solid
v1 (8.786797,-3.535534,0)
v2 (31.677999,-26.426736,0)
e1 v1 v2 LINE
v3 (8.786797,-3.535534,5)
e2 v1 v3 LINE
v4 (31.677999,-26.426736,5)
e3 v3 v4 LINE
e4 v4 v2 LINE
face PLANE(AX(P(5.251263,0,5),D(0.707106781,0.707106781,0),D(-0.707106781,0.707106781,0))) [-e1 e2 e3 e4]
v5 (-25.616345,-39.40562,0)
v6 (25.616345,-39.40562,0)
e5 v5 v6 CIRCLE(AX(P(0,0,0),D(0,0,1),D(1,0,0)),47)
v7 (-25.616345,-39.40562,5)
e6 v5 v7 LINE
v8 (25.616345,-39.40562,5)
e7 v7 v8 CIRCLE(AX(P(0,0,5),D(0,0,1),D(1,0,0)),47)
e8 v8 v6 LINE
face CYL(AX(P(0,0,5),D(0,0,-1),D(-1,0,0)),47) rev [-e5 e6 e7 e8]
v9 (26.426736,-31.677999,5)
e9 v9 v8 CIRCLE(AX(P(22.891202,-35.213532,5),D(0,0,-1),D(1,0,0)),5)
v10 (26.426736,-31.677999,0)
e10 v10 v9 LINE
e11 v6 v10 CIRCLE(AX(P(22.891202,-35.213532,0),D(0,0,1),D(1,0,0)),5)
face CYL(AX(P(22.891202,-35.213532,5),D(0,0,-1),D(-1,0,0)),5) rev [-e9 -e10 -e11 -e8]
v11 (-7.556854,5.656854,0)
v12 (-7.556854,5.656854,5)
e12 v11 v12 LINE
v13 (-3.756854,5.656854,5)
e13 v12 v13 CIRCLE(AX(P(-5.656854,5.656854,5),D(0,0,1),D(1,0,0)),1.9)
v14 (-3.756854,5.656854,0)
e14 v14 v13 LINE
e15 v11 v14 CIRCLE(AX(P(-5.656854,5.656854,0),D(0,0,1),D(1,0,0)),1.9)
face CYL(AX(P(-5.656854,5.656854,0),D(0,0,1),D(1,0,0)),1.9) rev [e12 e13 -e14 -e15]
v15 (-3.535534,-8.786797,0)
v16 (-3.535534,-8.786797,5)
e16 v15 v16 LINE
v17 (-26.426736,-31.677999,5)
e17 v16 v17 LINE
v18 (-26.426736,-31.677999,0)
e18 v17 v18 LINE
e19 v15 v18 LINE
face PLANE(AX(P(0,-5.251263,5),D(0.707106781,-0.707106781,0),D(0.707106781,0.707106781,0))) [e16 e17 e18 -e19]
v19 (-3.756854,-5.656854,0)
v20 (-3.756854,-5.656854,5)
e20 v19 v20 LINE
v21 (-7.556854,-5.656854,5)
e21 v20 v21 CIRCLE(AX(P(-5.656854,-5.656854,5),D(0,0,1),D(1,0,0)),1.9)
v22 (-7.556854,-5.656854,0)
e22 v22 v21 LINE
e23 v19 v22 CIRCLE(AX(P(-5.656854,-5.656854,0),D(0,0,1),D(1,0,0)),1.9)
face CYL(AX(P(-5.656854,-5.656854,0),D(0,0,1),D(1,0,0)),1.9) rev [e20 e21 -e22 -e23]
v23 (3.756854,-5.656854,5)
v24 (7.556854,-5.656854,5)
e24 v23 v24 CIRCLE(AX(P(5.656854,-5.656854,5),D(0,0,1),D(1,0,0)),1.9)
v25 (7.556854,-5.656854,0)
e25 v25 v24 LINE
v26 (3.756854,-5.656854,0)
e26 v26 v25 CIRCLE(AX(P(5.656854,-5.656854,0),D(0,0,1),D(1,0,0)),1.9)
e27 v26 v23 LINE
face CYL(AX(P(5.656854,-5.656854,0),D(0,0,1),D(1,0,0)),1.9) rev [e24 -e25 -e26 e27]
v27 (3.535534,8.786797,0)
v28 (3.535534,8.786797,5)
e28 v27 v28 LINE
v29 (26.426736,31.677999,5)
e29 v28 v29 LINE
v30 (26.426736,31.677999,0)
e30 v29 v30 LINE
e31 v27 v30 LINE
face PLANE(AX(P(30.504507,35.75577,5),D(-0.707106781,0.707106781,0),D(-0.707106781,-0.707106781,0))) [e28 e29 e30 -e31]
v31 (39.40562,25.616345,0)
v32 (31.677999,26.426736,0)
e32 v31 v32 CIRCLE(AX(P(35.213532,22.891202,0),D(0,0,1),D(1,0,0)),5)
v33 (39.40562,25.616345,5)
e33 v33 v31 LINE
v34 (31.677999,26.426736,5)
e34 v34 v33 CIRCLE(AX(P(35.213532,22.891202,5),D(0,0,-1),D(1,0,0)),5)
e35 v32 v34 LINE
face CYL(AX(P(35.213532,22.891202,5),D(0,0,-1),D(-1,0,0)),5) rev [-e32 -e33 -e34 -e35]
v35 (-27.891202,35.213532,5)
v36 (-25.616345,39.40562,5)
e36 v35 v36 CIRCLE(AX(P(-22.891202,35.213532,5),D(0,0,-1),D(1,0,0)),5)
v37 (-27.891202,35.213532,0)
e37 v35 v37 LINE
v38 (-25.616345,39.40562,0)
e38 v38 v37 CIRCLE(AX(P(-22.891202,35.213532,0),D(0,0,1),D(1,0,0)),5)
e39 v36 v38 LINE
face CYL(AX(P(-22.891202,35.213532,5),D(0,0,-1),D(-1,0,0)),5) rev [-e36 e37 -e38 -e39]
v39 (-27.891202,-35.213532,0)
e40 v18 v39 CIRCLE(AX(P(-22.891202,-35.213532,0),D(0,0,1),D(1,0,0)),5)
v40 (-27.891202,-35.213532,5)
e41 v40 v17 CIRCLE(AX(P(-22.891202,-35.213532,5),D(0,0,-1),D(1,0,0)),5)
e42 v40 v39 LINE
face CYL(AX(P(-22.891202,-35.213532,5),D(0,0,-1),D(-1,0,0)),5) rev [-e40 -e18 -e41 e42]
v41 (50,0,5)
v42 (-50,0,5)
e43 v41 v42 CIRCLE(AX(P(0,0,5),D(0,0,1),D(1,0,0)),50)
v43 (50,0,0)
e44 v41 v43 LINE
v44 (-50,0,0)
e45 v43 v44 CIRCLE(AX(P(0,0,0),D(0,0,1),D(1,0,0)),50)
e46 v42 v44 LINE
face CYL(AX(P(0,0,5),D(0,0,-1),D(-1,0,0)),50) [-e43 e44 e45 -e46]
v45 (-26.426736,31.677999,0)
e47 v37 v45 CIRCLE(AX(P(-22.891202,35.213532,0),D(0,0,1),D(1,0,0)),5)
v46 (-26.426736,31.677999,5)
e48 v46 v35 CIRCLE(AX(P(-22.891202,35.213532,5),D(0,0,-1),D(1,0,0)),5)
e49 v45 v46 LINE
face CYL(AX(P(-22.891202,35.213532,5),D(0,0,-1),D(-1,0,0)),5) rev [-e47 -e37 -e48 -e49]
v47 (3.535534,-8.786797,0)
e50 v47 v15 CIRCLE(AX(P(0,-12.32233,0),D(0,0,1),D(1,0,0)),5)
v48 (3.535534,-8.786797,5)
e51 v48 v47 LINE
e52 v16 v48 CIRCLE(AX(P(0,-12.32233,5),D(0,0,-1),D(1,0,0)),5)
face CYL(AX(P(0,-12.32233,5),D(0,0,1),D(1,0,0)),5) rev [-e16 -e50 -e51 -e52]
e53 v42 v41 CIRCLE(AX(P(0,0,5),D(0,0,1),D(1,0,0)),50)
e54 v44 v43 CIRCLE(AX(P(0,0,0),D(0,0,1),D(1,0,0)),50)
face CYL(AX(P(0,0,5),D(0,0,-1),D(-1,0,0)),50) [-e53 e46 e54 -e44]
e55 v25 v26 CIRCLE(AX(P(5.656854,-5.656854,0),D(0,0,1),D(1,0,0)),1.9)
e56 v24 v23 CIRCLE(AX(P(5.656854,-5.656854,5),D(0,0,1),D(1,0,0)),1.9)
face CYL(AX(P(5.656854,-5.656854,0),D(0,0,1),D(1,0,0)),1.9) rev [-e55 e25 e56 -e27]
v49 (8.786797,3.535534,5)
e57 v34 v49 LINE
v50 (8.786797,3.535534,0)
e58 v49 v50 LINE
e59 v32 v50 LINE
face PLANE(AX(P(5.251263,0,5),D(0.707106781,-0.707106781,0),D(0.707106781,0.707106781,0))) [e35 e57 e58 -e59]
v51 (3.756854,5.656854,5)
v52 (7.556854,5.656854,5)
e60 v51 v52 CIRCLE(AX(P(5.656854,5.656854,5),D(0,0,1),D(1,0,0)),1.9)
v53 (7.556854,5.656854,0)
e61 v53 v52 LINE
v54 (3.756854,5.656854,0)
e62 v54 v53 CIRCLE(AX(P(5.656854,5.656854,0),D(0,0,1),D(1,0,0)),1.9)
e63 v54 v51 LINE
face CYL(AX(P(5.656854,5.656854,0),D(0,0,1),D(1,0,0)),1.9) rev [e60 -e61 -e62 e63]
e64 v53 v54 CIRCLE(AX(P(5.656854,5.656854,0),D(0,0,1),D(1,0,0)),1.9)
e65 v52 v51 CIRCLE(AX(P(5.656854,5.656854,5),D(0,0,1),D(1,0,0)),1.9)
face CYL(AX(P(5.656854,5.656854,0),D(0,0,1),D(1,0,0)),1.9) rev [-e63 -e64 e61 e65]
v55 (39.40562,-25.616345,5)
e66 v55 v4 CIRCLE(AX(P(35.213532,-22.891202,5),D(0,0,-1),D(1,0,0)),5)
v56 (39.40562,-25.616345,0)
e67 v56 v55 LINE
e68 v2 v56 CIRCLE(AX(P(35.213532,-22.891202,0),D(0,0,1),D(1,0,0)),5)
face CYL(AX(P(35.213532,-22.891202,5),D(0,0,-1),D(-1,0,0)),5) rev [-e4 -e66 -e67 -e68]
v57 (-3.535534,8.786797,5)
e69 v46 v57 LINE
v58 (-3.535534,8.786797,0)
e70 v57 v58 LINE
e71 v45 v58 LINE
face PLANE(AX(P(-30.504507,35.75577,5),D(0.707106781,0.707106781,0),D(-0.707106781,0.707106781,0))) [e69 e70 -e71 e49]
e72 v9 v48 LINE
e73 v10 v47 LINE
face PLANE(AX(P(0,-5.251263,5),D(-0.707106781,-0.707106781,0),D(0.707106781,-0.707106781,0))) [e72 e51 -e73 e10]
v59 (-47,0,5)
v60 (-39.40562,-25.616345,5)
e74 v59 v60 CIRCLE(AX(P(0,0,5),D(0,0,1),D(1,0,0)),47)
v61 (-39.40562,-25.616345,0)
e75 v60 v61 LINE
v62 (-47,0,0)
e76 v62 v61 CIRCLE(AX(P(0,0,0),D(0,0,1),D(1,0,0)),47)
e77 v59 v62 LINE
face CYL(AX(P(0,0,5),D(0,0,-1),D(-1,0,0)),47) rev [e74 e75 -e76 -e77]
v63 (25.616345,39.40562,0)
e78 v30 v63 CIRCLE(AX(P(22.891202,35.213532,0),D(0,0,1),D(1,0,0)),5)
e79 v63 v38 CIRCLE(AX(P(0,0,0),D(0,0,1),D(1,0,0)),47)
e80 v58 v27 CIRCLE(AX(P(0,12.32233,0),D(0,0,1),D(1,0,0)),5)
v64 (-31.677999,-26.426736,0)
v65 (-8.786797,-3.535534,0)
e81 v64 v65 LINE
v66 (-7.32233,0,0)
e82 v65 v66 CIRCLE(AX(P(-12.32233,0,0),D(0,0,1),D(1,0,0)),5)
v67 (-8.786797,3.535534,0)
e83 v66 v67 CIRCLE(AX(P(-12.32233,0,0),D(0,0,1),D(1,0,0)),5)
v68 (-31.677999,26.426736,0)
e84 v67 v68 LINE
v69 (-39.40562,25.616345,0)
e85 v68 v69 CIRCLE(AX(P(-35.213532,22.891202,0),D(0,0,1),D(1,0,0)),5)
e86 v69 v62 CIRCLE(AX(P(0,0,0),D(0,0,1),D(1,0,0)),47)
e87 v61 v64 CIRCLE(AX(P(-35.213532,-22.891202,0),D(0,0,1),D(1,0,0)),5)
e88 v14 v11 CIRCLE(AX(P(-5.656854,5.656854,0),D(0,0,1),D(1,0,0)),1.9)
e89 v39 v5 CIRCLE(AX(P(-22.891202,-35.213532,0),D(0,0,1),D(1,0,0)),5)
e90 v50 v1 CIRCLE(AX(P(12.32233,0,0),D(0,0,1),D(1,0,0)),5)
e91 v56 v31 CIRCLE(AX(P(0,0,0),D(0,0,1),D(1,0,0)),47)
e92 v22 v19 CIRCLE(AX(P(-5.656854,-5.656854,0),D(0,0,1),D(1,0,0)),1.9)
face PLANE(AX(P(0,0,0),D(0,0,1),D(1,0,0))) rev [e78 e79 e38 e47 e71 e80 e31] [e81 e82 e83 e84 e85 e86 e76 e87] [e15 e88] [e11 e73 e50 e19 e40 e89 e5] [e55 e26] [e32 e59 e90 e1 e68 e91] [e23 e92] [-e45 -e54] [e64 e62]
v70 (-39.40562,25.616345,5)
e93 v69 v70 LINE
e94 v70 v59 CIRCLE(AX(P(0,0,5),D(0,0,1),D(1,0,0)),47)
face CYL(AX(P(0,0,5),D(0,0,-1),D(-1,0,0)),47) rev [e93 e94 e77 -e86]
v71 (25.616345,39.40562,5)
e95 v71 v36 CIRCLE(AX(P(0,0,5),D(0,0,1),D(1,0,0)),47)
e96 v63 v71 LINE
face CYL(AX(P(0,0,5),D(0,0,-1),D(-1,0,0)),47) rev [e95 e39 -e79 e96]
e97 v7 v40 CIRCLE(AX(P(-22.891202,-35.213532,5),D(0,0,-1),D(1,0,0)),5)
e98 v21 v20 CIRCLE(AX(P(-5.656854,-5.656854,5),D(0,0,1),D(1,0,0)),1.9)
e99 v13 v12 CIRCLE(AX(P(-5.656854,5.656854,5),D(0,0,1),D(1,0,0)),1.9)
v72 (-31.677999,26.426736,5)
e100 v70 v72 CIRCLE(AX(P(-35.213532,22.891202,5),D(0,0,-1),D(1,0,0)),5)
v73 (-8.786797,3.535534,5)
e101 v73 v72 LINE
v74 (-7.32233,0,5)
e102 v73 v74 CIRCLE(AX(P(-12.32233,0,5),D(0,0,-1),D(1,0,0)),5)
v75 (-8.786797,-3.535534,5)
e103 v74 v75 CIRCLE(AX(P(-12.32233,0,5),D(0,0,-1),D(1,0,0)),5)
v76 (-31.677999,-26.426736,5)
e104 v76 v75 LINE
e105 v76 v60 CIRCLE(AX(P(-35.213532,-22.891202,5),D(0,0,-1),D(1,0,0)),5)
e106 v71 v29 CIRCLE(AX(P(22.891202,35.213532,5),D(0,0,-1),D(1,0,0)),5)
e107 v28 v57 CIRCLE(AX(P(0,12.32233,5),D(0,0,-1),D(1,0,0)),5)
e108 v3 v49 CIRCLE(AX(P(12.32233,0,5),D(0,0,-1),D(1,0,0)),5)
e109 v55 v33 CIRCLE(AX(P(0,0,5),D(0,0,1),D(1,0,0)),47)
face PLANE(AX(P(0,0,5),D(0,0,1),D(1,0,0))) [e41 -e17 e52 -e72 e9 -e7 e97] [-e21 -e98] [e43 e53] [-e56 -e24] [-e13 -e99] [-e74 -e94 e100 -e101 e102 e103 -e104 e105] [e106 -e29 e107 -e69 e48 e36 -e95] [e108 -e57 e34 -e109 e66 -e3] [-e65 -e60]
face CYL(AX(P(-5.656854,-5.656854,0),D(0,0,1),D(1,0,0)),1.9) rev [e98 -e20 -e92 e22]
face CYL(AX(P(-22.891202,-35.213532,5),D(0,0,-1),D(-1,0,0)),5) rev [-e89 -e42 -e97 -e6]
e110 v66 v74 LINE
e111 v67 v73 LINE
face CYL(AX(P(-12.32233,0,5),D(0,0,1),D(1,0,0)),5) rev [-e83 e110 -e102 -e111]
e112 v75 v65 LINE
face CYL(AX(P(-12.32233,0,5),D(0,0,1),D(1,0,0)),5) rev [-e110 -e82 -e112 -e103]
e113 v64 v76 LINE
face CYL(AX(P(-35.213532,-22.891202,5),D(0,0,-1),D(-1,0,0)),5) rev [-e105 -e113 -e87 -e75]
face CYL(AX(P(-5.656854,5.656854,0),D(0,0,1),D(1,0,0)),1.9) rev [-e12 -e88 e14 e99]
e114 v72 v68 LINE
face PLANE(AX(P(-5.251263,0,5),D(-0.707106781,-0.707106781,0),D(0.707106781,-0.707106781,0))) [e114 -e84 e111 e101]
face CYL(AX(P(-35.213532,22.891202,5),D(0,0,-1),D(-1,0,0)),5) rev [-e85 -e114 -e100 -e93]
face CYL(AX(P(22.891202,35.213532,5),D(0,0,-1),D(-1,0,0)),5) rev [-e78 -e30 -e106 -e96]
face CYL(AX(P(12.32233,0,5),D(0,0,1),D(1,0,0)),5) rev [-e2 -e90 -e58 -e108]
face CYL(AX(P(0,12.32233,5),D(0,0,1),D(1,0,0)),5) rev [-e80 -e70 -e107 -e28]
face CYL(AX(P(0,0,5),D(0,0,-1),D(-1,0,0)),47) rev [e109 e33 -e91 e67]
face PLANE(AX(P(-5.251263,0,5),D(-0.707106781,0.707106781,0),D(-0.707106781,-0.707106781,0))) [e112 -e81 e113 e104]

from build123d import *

# Parameters (mm, degrees)
SKETCH1_R           = 50
BOSS_EXTRUDE1_DEPTH = 5
FILLET1_R           = 5
SKETCH2_R           = 1.9
CUT_EXTRUDE1_DEPTH  = 5


with BuildPart() as part:
    # Sketch1 → Boss-Extrude1 (new body)
    with BuildSketch(Plane.XY):
        Circle(SKETCH1_R)
        with BuildLine():
            Line((30.504506916, 35.755769574), (0, 5.251262658))
            Line((0, 5.251262658), (-30.504506916, 35.755769574))
            ThreePointArc((-30.504506916, 35.755769574), (0, 47), (30.504506916, 35.755769574))
        make_face(mode=Mode.SUBTRACT)
        with BuildLine():
            Line((5.251262658, 0), (35.755769574, 30.504506916))
            ThreePointArc((35.755769574, 30.504506916), (47, 0), (35.755769574, -30.504506916))
            Line((35.755769574, -30.504506916), (5.251262658, 0))
        make_face(mode=Mode.SUBTRACT)
        with BuildLine():
            Line((0, -5.251262658), (30.504506916, -35.755769574))
            ThreePointArc((30.504506916, -35.755769574), (0, -47), (-30.504506916, -35.755769574))
            Line((-30.504506916, -35.755769574), (0, -5.251262658))
        make_face(mode=Mode.SUBTRACT)
        with BuildLine():
            Line((-5.251262658, 0), (-35.755769574, -30.504506916))
            ThreePointArc((-35.755769574, -30.504506916), (-47, 0), (-35.755769574, 30.504506916))
            Line((-35.755769574, 30.504506916), (-5.251262658, 0))
        make_face(mode=Mode.SUBTRACT)
    extrude(amount=BOSS_EXTRUDE1_DEPTH)

    # Fillet1
    fillet1_edges = [part.edges().sort_by_distance(p)[0] for p in [
        (-5.251262658, 0, 2.5),
        (-35.755769574, 30.504506916, 2.5),
        (-35.755769574, -30.504506916, 2.5),
        (35.755769574, -30.504506916, 2.5),
        (35.755769574, 30.504506916, 2.5),
        (5.251262658, 0, 2.5),
        (-30.504506916, -35.755769574, 2.5),
        (30.504506916, -35.755769574, 2.5),
        (0, -5.251262658, 2.5),
        (30.504506916, 35.755769574, 2.5),
        (-30.504506916, 35.755769574, 2.5),
        (0, 5.251262658, 2.5),
    ]]
    fillet(fillet1_edges, radius=FILLET1_R)

    # Sketch2 → Cut-Extrude1 (cut)
    with BuildSketch(Plane.XY.offset(5)):
        with Locations((5.656854249, -5.656854249)):
            Circle(SKETCH2_R)
        with Locations((5.656854249, 5.656854249)):
            Circle(SKETCH2_R)
        with Locations((-5.656854249, 5.656854249)):
            Circle(SKETCH2_R)
        with Locations((-5.656854249, -5.656854249)):
            Circle(SKETCH2_R)
    extrude(amount=-CUT_EXTRUDE1_DEPTH, mode=Mode.SUBTRACT)


solid = part.part
